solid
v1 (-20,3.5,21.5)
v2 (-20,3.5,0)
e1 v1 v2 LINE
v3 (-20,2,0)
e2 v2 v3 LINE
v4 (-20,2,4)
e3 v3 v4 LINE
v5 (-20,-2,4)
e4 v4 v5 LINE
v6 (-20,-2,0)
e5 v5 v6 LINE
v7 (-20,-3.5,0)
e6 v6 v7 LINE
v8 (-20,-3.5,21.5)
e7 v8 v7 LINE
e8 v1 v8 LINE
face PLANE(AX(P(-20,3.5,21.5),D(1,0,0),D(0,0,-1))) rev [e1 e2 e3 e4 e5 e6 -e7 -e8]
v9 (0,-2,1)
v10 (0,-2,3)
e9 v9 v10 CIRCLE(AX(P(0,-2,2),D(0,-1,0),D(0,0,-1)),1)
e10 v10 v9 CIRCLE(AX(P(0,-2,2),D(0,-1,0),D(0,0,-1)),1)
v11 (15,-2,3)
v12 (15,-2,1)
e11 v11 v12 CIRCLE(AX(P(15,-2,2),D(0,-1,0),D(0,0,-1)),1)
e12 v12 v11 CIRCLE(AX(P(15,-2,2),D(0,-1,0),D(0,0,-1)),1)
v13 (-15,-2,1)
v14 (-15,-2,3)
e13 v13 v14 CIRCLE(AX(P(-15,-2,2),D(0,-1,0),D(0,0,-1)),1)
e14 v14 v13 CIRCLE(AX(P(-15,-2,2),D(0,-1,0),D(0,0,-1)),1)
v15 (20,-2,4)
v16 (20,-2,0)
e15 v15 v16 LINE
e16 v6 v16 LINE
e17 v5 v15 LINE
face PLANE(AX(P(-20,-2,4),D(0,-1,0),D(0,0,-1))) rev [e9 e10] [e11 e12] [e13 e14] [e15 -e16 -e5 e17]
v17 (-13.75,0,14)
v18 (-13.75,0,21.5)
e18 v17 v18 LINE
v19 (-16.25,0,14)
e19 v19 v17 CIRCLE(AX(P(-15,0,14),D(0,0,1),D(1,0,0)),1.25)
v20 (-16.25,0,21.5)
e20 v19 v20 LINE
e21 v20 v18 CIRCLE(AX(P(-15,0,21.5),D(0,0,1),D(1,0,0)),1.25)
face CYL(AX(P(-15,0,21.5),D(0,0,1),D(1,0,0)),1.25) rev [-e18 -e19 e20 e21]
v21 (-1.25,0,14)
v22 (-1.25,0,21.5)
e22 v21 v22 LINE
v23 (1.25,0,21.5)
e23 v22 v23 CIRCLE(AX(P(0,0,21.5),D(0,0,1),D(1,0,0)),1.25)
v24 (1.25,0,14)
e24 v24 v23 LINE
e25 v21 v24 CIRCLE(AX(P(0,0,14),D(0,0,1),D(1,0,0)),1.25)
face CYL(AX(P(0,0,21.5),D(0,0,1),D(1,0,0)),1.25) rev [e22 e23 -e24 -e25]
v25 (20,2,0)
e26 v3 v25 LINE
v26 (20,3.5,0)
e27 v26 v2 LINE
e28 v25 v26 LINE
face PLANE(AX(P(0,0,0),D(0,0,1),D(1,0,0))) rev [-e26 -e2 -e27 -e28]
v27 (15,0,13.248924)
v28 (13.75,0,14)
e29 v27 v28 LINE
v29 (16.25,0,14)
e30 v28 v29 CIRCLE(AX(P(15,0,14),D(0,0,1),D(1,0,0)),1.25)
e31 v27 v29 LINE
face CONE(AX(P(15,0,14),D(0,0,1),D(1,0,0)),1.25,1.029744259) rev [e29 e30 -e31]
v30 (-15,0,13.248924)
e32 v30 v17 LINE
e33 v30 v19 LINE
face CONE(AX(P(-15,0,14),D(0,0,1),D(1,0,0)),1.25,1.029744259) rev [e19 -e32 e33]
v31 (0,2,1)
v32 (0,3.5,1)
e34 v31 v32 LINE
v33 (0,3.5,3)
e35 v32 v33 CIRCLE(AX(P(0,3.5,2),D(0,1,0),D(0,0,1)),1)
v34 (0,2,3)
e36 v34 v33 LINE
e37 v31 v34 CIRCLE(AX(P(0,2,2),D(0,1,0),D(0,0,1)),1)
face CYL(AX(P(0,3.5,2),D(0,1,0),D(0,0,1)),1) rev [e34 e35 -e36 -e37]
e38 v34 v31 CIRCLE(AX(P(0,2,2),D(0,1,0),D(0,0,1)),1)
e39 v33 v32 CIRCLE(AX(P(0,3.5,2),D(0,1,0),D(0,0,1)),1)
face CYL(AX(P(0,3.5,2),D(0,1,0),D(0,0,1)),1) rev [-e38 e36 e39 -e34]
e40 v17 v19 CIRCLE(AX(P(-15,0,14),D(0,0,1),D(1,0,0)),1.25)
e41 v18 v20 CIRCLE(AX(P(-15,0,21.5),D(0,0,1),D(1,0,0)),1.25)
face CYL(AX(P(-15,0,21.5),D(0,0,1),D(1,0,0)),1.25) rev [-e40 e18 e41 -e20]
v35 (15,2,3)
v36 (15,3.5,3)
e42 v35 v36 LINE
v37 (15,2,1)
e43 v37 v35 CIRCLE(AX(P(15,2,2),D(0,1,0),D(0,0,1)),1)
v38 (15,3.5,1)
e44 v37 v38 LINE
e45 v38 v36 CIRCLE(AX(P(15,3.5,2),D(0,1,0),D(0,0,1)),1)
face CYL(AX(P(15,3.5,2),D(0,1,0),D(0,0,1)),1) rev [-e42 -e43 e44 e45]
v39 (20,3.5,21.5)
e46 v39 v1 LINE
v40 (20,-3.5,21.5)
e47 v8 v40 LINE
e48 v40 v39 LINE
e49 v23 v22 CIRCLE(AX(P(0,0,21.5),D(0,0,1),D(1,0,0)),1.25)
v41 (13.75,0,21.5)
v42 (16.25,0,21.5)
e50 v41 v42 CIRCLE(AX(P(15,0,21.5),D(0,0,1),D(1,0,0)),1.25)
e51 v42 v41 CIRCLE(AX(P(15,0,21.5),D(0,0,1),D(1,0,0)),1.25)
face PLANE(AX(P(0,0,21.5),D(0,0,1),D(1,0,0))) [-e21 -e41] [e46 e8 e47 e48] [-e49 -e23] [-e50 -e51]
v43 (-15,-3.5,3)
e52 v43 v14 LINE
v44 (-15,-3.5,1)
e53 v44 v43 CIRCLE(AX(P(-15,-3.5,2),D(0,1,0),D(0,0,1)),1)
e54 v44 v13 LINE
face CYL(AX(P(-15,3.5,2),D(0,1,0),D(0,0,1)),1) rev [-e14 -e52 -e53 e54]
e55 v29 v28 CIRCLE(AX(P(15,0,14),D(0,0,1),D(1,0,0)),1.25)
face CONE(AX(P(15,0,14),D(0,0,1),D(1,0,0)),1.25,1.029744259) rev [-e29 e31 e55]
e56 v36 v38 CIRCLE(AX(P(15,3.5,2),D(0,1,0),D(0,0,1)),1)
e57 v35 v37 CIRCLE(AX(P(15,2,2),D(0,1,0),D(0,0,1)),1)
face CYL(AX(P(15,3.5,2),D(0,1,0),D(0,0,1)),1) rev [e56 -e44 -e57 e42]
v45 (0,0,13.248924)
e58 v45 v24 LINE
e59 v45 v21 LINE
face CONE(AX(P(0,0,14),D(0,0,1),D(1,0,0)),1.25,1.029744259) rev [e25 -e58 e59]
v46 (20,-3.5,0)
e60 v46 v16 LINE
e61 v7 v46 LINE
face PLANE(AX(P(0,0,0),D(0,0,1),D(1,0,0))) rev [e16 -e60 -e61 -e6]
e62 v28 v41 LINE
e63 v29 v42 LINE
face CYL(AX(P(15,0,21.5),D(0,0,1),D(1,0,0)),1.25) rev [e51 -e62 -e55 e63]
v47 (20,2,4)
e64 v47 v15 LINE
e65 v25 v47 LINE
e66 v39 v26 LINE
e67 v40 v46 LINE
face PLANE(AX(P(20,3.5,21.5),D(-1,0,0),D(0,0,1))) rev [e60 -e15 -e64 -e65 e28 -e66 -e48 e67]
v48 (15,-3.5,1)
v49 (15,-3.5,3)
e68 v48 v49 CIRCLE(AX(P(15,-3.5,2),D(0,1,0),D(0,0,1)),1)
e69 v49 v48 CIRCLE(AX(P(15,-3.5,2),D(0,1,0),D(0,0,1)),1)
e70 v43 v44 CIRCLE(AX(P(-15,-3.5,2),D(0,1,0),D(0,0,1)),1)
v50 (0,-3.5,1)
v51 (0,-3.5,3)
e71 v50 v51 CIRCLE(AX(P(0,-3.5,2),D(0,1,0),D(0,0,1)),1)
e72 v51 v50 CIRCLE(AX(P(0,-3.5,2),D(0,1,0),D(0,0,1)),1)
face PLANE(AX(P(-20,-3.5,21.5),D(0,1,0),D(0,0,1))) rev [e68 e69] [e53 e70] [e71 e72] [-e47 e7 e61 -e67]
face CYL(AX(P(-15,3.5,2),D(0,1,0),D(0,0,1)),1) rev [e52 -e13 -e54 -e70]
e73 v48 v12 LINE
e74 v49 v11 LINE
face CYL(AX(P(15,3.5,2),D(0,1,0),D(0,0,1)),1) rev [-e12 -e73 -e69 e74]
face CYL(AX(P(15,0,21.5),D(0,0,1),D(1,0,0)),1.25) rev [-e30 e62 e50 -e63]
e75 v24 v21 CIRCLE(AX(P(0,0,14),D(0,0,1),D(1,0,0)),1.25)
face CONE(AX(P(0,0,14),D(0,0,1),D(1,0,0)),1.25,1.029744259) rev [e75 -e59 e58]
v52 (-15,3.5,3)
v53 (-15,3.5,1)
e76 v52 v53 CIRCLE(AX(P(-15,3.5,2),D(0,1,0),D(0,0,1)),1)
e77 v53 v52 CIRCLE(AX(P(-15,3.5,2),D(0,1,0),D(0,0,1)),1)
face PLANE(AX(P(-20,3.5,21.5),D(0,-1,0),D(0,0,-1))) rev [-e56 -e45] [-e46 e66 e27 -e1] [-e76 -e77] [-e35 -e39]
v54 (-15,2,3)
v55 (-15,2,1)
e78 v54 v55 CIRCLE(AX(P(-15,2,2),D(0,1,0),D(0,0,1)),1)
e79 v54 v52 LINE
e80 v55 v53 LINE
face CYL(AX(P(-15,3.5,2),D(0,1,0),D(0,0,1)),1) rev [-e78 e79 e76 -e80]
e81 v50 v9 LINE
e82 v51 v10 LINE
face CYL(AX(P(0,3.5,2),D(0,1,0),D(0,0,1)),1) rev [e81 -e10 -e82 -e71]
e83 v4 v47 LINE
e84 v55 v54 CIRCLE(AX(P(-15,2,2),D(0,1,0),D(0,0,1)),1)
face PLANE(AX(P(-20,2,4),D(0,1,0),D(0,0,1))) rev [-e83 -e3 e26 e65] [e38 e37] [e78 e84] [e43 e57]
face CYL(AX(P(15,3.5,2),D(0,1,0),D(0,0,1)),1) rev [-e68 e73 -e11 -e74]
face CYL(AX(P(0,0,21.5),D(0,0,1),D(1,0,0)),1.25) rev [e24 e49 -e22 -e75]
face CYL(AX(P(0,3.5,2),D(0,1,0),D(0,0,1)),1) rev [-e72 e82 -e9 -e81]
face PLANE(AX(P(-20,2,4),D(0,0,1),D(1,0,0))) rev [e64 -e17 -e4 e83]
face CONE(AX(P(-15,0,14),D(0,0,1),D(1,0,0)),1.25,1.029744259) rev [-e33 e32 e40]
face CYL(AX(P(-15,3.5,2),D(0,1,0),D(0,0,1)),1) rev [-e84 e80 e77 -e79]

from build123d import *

# Parameters (mm, degrees)
SKETCH_1_W             = 40
SKETCH_1_H             = 7
EXTRUDE_1_DEPTH        = 21.5
HOLE_WIZARD_M3_1_D     = 2.5
HOLE_WIZARD_M3_1_DEPTH = 7.5
HOLE_WIZARD_M3_1_TIP   = 0.751075774
SKETCH_4_W             = 4
SKETCH_4_H             = 4
CUT_EXTRUDE_1_DEPTH    = 46.546679352
MM_1_D                 = 2


with BuildPart() as part:
    # 草图1 → 凸台-拉伸1 (new body)
    with BuildSketch(Plane.XY):
        Rectangle(SKETCH_1_W, SKETCH_1_H)
    extrude(amount=EXTRUDE_1_DEPTH)

    # M3 螺纹孔1
    with Locations(Plane.XY.offset(21.5)):
        with Locations((-15, 0), (0, 0), (15, 0)):
            Hole(HOLE_WIZARD_M3_1_D / 2, depth=HOLE_WIZARD_M3_1_DEPTH)
            with Locations((0, 0, -(HOLE_WIZARD_M3_1_DEPTH + HOLE_WIZARD_M3_1_TIP / 2))):  # 118° drill point
                Cone(0, HOLE_WIZARD_M3_1_D / 2, HOLE_WIZARD_M3_1_TIP, mode=Mode.SUBTRACT)

    # 草图4 → 切除-拉伸1 (cut, through all)
    with BuildSketch(Plane(origin=(20, 0, 0), x_dir=(0, 0, -1), z_dir=(1, 0, 0))):
        with Locations((-2, 0)):
            Rectangle(SKETCH_4_W, SKETCH_4_H)
    extrude(amount=-CUT_EXTRUDE_1_DEPTH, mode=Mode.SUBTRACT)

    # 大小mm 暗销孔1 (through all)
    with Locations(Plane(origin=(0, 3.5, 0), x_dir=(1, 0, 0), z_dir=(0, 1, 0))):
        with Locations((-15, -2), (0, -2), (15, -2)):
            Hole(MM_1_D / 2)


solid = part.part
